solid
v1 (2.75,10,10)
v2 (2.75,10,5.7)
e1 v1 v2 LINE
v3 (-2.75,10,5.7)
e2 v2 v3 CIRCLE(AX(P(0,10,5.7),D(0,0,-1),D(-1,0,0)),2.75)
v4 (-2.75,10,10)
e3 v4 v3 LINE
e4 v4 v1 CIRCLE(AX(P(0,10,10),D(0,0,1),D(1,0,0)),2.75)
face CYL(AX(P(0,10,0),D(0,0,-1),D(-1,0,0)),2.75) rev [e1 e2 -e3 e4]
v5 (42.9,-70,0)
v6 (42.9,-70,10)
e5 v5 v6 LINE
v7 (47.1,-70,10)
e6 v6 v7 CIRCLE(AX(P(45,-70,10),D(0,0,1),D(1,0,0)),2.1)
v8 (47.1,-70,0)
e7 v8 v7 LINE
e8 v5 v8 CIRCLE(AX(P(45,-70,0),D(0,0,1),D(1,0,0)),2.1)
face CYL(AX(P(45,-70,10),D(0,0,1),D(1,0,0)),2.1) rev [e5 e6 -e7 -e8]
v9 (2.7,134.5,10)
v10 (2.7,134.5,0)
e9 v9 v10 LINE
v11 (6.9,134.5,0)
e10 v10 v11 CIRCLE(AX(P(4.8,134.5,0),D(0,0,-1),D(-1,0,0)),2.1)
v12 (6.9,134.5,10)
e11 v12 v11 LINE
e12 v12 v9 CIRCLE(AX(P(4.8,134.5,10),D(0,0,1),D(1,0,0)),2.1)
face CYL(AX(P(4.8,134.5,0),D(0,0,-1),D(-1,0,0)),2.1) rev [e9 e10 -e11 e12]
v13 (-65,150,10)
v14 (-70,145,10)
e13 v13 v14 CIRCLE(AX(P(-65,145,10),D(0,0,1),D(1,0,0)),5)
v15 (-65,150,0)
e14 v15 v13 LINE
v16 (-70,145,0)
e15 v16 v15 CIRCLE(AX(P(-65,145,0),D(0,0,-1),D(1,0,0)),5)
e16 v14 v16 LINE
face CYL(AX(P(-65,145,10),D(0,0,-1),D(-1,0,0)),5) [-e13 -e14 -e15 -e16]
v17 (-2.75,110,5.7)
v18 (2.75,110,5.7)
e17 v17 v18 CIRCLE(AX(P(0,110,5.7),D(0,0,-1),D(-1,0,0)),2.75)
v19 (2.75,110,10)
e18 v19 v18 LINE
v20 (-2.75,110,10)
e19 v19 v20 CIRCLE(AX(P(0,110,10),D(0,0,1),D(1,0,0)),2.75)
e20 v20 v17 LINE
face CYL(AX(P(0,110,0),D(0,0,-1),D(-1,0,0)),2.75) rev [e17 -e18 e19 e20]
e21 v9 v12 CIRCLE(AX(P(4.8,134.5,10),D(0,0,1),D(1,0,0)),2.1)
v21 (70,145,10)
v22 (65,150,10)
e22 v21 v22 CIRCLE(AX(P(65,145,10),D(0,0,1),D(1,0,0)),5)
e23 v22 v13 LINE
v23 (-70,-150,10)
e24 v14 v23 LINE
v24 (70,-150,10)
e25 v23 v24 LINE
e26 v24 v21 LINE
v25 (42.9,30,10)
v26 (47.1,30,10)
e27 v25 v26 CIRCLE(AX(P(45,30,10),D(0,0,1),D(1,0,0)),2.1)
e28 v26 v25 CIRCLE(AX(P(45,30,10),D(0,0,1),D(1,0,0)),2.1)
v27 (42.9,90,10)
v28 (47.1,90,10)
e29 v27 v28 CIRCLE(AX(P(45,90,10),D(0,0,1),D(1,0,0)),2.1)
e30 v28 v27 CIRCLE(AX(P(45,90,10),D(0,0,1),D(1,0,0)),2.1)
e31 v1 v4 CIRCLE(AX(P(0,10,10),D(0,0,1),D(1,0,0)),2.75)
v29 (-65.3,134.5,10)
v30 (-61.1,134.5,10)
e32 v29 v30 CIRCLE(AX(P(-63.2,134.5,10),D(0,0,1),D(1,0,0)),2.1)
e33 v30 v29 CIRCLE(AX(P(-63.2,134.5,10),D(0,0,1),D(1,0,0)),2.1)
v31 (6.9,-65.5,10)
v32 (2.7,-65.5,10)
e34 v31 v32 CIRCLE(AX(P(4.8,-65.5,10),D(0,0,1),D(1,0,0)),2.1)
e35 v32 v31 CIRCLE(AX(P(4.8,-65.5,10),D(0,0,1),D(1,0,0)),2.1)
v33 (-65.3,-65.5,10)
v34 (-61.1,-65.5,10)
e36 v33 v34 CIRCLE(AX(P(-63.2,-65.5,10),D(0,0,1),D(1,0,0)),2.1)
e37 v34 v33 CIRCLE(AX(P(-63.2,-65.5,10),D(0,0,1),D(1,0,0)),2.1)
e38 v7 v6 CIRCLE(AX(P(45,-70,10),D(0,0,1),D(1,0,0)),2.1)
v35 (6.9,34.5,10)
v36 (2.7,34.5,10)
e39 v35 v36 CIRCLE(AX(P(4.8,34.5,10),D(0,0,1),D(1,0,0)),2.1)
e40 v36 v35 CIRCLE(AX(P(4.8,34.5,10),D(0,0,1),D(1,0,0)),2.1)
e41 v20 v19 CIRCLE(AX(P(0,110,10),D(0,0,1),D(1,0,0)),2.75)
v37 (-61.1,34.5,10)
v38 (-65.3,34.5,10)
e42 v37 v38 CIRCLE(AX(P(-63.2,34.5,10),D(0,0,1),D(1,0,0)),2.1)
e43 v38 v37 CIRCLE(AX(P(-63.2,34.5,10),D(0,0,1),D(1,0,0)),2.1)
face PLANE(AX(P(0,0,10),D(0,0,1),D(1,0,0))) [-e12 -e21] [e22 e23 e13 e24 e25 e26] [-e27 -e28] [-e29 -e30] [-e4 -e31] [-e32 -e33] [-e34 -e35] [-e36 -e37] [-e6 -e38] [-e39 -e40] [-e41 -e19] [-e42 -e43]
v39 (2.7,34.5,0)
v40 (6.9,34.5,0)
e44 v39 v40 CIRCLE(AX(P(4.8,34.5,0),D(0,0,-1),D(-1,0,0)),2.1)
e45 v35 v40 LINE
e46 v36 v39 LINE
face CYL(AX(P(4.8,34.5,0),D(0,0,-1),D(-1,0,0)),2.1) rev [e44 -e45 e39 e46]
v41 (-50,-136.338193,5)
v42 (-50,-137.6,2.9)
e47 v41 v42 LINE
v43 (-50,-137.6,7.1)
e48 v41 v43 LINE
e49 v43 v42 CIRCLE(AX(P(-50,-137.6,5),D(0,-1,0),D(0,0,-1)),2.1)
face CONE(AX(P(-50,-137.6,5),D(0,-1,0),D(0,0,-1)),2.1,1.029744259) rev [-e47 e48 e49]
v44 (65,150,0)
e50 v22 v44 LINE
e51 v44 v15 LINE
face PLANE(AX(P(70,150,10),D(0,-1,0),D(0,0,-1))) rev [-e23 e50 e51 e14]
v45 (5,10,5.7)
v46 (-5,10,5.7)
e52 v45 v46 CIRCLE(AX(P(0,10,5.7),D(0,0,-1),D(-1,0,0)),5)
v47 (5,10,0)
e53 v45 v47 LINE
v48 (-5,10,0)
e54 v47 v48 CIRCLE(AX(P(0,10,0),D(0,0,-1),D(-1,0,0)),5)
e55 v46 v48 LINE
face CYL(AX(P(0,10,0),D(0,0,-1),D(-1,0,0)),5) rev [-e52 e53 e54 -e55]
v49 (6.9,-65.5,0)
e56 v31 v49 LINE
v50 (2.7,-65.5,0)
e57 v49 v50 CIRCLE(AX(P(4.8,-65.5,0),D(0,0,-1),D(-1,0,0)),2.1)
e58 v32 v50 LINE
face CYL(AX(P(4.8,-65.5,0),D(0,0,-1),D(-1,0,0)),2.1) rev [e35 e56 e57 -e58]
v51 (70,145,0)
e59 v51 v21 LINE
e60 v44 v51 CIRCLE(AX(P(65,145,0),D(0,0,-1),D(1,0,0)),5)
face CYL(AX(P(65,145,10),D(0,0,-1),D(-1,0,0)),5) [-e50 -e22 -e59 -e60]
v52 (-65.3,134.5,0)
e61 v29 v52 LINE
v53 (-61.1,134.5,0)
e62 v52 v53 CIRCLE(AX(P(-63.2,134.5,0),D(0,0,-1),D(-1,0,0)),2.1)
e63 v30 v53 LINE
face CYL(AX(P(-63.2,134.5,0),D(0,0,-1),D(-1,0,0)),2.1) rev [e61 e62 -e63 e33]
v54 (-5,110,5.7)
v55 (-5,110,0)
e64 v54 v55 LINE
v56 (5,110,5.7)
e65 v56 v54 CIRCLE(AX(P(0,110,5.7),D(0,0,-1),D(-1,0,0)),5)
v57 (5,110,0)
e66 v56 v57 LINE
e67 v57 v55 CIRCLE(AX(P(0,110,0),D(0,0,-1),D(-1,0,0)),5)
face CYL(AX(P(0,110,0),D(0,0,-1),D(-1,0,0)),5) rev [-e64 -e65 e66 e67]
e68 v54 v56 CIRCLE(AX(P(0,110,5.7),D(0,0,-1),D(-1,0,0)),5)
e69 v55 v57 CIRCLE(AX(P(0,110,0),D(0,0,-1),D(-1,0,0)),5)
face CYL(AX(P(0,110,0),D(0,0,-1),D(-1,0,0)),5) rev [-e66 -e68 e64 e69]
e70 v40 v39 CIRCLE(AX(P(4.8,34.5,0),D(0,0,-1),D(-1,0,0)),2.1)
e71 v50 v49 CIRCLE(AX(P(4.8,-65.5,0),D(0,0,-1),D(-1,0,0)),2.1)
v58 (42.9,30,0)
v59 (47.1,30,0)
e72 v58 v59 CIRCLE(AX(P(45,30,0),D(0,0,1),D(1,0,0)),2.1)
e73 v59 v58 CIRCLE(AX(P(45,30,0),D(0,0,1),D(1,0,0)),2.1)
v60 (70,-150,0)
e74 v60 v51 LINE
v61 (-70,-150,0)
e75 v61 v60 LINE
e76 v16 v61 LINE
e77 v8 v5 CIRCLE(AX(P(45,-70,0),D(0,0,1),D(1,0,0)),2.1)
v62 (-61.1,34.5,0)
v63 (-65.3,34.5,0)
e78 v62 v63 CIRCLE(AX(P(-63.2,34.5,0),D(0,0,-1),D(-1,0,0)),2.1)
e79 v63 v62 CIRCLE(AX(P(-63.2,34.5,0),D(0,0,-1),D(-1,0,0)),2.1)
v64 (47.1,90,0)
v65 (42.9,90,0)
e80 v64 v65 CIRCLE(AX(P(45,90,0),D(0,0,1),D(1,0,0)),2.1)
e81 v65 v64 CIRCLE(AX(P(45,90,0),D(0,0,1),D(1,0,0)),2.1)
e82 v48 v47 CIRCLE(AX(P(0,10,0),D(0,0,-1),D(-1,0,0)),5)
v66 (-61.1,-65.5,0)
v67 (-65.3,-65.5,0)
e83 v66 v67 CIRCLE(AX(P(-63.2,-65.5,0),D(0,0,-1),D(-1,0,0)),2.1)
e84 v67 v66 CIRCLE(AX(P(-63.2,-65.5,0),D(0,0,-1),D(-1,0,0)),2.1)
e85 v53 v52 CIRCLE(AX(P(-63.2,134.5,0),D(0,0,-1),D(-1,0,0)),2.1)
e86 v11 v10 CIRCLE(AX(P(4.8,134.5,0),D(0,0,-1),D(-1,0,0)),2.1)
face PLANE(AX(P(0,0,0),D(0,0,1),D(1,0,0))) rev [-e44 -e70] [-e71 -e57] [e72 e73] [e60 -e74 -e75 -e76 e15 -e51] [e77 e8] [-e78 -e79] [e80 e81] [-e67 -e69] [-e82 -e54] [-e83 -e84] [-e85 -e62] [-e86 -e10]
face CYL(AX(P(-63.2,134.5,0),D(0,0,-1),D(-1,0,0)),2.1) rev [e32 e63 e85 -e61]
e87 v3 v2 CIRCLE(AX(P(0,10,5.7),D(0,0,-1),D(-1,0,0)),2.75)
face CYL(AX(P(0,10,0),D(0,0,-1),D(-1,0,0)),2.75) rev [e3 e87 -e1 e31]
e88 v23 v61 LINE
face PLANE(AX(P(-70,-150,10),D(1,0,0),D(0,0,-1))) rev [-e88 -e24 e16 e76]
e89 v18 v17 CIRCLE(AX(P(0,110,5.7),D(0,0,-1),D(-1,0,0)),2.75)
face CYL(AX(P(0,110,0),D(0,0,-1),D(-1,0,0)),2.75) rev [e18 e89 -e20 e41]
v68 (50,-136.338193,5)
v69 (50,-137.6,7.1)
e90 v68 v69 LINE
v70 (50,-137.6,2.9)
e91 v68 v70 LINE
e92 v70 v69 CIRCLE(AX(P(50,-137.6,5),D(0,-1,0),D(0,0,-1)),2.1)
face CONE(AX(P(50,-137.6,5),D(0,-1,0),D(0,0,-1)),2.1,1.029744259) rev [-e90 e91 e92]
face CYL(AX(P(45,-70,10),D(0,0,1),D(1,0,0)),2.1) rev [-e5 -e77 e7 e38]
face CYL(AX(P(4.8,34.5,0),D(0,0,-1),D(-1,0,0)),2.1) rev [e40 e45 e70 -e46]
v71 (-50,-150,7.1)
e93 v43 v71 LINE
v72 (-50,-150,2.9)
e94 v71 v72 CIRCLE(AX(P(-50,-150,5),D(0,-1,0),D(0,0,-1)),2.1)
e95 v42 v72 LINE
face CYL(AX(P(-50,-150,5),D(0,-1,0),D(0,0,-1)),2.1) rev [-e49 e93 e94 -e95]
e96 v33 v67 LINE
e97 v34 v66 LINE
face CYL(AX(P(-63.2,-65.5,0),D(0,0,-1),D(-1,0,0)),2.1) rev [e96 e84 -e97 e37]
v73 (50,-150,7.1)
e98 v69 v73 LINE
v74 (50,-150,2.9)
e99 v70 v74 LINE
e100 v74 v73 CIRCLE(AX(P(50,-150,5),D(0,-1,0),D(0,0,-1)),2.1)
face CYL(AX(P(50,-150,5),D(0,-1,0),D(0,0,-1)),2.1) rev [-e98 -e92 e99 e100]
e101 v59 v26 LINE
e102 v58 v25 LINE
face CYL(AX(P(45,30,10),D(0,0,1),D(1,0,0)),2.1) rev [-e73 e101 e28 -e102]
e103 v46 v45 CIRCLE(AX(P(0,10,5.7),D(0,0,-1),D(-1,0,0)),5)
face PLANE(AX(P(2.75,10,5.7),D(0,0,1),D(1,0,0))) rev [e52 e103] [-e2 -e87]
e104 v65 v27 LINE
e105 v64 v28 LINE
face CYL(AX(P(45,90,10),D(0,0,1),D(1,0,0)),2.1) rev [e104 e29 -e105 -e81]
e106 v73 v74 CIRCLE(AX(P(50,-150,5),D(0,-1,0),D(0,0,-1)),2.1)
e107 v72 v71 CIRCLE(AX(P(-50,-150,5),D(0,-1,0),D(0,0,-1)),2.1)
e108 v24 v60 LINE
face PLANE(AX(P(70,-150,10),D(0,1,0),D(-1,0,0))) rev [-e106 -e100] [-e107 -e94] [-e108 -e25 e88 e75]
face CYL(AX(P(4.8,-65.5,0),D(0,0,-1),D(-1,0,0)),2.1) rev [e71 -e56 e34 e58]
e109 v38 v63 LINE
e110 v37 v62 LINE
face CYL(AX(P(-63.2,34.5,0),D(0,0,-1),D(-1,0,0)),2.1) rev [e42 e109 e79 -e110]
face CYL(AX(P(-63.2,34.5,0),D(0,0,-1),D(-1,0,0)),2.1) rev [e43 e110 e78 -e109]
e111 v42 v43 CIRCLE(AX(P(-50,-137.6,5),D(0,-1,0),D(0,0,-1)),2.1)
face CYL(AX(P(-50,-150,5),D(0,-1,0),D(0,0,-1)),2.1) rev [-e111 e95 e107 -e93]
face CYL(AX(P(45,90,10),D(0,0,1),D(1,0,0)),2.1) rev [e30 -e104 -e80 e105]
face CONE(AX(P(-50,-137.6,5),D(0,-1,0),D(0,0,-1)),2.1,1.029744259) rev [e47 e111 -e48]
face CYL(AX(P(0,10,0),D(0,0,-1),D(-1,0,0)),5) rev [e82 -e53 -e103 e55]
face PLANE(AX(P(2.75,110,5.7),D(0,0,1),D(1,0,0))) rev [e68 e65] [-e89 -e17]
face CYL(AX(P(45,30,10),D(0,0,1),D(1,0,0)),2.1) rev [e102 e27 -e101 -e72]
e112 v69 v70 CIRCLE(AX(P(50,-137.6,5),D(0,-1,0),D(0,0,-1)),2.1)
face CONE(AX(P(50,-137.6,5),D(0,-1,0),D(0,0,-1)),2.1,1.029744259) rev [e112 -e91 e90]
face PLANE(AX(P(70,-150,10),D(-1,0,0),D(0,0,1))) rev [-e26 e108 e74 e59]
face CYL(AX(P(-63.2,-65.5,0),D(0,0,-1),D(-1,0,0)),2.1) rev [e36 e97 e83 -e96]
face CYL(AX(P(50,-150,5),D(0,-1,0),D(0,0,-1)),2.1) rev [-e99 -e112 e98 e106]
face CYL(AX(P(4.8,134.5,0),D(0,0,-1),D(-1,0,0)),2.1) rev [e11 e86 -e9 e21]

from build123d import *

# Parameters (mm, degrees)
SKETCH_1_W                = 140
SKETCH_1_H                = 300
EXTRUDE_1_DEPTH           = 10
HOLE_WIZARD_1_D           = 5.5
HOLE_WIZARD_1_DEPTH       = 14.4
HOLE_WIZARD_1_CBORE_D     = 10
HOLE_WIZARD_1_CBORE_DEPTH = 5.7
HOLE_WIZARD_1_TIP         = 1.652366702
HOLE_WIZARD_M5_1_D        = 4.2
HOLE_WIZARD_M5_2_D        = 4.2
HOLE_WIZARD_M5_2_DEPTH    = 12.4
HOLE_WIZARD_M5_2_TIP      = 1.2618073
HOLE_WIZARD_M5_3_D        = 4.2
FILLET_1_R                = 5


with BuildPart() as part:
    # 草图1 → 凸台-拉伸1 (new body)
    with BuildSketch(Plane.XY):
        Rectangle(SKETCH_1_W, SKETCH_1_H)
    extrude(amount=EXTRUDE_1_DEPTH)

    # 打孔尺寸(%根据)内六角圆柱头螺钉的类型1
    with Locations(Plane(origin=(0, 0, 0), x_dir=(-1, 0, 0), z_dir=(0, 0, -1))):
        with Locations((0, 110), (0, 10)):
            CounterBoreHole(HOLE_WIZARD_1_D / 2, HOLE_WIZARD_1_CBORE_D / 2, HOLE_WIZARD_1_CBORE_DEPTH, depth=HOLE_WIZARD_1_DEPTH)
            with Locations((0, 0, -(HOLE_WIZARD_1_DEPTH + HOLE_WIZARD_1_TIP / 2))):  # 118° drill point
                Cone(0, HOLE_WIZARD_1_D / 2, HOLE_WIZARD_1_TIP, mode=Mode.SUBTRACT)

    # M5 螺纹孔1 (through all)
    with Locations(Plane(origin=(0, 0, 0), x_dir=(-1, 0, 0), z_dir=(0, 0, -1))):
        with Locations((-4.800000353, -65.5), (63.199999647, -65.5), (-4.800000353, 34.5), (63.199999647, 34.5), (-4.800000353, 134.5), (63.199999647, 134.5)):
            Hole(HOLE_WIZARD_M5_1_D / 2)

    # M5 螺纹孔2
    with Locations(Plane(origin=(0, -150, 0), x_dir=(-1, 0, 0), z_dir=(0, -1, 0))):
        with Locations((-50, -5), (50, -5)):
            Hole(HOLE_WIZARD_M5_2_D / 2, depth=HOLE_WIZARD_M5_2_DEPTH)
            with Locations((0, 0, -(HOLE_WIZARD_M5_2_DEPTH + HOLE_WIZARD_M5_2_TIP / 2))):  # 118° drill point
                Cone(0, HOLE_WIZARD_M5_2_D / 2, HOLE_WIZARD_M5_2_TIP, mode=Mode.SUBTRACT)

    # M5 螺纹孔3 (through all)
    with Locations(Plane.XY.offset(10)):
        with Locations((45, 90), (45, 30), (45, -70)):
            Hole(HOLE_WIZARD_M5_3_D / 2)

    # 圆角1
    fillet_1_edges = [part.edges().sort_by_distance(p)[0] for p in [
        (-70, 150, 5),
        (70, 150, 5),
    ]]
    fillet(fillet_1_edges, radius=FILLET_1_R)


solid = part.part
